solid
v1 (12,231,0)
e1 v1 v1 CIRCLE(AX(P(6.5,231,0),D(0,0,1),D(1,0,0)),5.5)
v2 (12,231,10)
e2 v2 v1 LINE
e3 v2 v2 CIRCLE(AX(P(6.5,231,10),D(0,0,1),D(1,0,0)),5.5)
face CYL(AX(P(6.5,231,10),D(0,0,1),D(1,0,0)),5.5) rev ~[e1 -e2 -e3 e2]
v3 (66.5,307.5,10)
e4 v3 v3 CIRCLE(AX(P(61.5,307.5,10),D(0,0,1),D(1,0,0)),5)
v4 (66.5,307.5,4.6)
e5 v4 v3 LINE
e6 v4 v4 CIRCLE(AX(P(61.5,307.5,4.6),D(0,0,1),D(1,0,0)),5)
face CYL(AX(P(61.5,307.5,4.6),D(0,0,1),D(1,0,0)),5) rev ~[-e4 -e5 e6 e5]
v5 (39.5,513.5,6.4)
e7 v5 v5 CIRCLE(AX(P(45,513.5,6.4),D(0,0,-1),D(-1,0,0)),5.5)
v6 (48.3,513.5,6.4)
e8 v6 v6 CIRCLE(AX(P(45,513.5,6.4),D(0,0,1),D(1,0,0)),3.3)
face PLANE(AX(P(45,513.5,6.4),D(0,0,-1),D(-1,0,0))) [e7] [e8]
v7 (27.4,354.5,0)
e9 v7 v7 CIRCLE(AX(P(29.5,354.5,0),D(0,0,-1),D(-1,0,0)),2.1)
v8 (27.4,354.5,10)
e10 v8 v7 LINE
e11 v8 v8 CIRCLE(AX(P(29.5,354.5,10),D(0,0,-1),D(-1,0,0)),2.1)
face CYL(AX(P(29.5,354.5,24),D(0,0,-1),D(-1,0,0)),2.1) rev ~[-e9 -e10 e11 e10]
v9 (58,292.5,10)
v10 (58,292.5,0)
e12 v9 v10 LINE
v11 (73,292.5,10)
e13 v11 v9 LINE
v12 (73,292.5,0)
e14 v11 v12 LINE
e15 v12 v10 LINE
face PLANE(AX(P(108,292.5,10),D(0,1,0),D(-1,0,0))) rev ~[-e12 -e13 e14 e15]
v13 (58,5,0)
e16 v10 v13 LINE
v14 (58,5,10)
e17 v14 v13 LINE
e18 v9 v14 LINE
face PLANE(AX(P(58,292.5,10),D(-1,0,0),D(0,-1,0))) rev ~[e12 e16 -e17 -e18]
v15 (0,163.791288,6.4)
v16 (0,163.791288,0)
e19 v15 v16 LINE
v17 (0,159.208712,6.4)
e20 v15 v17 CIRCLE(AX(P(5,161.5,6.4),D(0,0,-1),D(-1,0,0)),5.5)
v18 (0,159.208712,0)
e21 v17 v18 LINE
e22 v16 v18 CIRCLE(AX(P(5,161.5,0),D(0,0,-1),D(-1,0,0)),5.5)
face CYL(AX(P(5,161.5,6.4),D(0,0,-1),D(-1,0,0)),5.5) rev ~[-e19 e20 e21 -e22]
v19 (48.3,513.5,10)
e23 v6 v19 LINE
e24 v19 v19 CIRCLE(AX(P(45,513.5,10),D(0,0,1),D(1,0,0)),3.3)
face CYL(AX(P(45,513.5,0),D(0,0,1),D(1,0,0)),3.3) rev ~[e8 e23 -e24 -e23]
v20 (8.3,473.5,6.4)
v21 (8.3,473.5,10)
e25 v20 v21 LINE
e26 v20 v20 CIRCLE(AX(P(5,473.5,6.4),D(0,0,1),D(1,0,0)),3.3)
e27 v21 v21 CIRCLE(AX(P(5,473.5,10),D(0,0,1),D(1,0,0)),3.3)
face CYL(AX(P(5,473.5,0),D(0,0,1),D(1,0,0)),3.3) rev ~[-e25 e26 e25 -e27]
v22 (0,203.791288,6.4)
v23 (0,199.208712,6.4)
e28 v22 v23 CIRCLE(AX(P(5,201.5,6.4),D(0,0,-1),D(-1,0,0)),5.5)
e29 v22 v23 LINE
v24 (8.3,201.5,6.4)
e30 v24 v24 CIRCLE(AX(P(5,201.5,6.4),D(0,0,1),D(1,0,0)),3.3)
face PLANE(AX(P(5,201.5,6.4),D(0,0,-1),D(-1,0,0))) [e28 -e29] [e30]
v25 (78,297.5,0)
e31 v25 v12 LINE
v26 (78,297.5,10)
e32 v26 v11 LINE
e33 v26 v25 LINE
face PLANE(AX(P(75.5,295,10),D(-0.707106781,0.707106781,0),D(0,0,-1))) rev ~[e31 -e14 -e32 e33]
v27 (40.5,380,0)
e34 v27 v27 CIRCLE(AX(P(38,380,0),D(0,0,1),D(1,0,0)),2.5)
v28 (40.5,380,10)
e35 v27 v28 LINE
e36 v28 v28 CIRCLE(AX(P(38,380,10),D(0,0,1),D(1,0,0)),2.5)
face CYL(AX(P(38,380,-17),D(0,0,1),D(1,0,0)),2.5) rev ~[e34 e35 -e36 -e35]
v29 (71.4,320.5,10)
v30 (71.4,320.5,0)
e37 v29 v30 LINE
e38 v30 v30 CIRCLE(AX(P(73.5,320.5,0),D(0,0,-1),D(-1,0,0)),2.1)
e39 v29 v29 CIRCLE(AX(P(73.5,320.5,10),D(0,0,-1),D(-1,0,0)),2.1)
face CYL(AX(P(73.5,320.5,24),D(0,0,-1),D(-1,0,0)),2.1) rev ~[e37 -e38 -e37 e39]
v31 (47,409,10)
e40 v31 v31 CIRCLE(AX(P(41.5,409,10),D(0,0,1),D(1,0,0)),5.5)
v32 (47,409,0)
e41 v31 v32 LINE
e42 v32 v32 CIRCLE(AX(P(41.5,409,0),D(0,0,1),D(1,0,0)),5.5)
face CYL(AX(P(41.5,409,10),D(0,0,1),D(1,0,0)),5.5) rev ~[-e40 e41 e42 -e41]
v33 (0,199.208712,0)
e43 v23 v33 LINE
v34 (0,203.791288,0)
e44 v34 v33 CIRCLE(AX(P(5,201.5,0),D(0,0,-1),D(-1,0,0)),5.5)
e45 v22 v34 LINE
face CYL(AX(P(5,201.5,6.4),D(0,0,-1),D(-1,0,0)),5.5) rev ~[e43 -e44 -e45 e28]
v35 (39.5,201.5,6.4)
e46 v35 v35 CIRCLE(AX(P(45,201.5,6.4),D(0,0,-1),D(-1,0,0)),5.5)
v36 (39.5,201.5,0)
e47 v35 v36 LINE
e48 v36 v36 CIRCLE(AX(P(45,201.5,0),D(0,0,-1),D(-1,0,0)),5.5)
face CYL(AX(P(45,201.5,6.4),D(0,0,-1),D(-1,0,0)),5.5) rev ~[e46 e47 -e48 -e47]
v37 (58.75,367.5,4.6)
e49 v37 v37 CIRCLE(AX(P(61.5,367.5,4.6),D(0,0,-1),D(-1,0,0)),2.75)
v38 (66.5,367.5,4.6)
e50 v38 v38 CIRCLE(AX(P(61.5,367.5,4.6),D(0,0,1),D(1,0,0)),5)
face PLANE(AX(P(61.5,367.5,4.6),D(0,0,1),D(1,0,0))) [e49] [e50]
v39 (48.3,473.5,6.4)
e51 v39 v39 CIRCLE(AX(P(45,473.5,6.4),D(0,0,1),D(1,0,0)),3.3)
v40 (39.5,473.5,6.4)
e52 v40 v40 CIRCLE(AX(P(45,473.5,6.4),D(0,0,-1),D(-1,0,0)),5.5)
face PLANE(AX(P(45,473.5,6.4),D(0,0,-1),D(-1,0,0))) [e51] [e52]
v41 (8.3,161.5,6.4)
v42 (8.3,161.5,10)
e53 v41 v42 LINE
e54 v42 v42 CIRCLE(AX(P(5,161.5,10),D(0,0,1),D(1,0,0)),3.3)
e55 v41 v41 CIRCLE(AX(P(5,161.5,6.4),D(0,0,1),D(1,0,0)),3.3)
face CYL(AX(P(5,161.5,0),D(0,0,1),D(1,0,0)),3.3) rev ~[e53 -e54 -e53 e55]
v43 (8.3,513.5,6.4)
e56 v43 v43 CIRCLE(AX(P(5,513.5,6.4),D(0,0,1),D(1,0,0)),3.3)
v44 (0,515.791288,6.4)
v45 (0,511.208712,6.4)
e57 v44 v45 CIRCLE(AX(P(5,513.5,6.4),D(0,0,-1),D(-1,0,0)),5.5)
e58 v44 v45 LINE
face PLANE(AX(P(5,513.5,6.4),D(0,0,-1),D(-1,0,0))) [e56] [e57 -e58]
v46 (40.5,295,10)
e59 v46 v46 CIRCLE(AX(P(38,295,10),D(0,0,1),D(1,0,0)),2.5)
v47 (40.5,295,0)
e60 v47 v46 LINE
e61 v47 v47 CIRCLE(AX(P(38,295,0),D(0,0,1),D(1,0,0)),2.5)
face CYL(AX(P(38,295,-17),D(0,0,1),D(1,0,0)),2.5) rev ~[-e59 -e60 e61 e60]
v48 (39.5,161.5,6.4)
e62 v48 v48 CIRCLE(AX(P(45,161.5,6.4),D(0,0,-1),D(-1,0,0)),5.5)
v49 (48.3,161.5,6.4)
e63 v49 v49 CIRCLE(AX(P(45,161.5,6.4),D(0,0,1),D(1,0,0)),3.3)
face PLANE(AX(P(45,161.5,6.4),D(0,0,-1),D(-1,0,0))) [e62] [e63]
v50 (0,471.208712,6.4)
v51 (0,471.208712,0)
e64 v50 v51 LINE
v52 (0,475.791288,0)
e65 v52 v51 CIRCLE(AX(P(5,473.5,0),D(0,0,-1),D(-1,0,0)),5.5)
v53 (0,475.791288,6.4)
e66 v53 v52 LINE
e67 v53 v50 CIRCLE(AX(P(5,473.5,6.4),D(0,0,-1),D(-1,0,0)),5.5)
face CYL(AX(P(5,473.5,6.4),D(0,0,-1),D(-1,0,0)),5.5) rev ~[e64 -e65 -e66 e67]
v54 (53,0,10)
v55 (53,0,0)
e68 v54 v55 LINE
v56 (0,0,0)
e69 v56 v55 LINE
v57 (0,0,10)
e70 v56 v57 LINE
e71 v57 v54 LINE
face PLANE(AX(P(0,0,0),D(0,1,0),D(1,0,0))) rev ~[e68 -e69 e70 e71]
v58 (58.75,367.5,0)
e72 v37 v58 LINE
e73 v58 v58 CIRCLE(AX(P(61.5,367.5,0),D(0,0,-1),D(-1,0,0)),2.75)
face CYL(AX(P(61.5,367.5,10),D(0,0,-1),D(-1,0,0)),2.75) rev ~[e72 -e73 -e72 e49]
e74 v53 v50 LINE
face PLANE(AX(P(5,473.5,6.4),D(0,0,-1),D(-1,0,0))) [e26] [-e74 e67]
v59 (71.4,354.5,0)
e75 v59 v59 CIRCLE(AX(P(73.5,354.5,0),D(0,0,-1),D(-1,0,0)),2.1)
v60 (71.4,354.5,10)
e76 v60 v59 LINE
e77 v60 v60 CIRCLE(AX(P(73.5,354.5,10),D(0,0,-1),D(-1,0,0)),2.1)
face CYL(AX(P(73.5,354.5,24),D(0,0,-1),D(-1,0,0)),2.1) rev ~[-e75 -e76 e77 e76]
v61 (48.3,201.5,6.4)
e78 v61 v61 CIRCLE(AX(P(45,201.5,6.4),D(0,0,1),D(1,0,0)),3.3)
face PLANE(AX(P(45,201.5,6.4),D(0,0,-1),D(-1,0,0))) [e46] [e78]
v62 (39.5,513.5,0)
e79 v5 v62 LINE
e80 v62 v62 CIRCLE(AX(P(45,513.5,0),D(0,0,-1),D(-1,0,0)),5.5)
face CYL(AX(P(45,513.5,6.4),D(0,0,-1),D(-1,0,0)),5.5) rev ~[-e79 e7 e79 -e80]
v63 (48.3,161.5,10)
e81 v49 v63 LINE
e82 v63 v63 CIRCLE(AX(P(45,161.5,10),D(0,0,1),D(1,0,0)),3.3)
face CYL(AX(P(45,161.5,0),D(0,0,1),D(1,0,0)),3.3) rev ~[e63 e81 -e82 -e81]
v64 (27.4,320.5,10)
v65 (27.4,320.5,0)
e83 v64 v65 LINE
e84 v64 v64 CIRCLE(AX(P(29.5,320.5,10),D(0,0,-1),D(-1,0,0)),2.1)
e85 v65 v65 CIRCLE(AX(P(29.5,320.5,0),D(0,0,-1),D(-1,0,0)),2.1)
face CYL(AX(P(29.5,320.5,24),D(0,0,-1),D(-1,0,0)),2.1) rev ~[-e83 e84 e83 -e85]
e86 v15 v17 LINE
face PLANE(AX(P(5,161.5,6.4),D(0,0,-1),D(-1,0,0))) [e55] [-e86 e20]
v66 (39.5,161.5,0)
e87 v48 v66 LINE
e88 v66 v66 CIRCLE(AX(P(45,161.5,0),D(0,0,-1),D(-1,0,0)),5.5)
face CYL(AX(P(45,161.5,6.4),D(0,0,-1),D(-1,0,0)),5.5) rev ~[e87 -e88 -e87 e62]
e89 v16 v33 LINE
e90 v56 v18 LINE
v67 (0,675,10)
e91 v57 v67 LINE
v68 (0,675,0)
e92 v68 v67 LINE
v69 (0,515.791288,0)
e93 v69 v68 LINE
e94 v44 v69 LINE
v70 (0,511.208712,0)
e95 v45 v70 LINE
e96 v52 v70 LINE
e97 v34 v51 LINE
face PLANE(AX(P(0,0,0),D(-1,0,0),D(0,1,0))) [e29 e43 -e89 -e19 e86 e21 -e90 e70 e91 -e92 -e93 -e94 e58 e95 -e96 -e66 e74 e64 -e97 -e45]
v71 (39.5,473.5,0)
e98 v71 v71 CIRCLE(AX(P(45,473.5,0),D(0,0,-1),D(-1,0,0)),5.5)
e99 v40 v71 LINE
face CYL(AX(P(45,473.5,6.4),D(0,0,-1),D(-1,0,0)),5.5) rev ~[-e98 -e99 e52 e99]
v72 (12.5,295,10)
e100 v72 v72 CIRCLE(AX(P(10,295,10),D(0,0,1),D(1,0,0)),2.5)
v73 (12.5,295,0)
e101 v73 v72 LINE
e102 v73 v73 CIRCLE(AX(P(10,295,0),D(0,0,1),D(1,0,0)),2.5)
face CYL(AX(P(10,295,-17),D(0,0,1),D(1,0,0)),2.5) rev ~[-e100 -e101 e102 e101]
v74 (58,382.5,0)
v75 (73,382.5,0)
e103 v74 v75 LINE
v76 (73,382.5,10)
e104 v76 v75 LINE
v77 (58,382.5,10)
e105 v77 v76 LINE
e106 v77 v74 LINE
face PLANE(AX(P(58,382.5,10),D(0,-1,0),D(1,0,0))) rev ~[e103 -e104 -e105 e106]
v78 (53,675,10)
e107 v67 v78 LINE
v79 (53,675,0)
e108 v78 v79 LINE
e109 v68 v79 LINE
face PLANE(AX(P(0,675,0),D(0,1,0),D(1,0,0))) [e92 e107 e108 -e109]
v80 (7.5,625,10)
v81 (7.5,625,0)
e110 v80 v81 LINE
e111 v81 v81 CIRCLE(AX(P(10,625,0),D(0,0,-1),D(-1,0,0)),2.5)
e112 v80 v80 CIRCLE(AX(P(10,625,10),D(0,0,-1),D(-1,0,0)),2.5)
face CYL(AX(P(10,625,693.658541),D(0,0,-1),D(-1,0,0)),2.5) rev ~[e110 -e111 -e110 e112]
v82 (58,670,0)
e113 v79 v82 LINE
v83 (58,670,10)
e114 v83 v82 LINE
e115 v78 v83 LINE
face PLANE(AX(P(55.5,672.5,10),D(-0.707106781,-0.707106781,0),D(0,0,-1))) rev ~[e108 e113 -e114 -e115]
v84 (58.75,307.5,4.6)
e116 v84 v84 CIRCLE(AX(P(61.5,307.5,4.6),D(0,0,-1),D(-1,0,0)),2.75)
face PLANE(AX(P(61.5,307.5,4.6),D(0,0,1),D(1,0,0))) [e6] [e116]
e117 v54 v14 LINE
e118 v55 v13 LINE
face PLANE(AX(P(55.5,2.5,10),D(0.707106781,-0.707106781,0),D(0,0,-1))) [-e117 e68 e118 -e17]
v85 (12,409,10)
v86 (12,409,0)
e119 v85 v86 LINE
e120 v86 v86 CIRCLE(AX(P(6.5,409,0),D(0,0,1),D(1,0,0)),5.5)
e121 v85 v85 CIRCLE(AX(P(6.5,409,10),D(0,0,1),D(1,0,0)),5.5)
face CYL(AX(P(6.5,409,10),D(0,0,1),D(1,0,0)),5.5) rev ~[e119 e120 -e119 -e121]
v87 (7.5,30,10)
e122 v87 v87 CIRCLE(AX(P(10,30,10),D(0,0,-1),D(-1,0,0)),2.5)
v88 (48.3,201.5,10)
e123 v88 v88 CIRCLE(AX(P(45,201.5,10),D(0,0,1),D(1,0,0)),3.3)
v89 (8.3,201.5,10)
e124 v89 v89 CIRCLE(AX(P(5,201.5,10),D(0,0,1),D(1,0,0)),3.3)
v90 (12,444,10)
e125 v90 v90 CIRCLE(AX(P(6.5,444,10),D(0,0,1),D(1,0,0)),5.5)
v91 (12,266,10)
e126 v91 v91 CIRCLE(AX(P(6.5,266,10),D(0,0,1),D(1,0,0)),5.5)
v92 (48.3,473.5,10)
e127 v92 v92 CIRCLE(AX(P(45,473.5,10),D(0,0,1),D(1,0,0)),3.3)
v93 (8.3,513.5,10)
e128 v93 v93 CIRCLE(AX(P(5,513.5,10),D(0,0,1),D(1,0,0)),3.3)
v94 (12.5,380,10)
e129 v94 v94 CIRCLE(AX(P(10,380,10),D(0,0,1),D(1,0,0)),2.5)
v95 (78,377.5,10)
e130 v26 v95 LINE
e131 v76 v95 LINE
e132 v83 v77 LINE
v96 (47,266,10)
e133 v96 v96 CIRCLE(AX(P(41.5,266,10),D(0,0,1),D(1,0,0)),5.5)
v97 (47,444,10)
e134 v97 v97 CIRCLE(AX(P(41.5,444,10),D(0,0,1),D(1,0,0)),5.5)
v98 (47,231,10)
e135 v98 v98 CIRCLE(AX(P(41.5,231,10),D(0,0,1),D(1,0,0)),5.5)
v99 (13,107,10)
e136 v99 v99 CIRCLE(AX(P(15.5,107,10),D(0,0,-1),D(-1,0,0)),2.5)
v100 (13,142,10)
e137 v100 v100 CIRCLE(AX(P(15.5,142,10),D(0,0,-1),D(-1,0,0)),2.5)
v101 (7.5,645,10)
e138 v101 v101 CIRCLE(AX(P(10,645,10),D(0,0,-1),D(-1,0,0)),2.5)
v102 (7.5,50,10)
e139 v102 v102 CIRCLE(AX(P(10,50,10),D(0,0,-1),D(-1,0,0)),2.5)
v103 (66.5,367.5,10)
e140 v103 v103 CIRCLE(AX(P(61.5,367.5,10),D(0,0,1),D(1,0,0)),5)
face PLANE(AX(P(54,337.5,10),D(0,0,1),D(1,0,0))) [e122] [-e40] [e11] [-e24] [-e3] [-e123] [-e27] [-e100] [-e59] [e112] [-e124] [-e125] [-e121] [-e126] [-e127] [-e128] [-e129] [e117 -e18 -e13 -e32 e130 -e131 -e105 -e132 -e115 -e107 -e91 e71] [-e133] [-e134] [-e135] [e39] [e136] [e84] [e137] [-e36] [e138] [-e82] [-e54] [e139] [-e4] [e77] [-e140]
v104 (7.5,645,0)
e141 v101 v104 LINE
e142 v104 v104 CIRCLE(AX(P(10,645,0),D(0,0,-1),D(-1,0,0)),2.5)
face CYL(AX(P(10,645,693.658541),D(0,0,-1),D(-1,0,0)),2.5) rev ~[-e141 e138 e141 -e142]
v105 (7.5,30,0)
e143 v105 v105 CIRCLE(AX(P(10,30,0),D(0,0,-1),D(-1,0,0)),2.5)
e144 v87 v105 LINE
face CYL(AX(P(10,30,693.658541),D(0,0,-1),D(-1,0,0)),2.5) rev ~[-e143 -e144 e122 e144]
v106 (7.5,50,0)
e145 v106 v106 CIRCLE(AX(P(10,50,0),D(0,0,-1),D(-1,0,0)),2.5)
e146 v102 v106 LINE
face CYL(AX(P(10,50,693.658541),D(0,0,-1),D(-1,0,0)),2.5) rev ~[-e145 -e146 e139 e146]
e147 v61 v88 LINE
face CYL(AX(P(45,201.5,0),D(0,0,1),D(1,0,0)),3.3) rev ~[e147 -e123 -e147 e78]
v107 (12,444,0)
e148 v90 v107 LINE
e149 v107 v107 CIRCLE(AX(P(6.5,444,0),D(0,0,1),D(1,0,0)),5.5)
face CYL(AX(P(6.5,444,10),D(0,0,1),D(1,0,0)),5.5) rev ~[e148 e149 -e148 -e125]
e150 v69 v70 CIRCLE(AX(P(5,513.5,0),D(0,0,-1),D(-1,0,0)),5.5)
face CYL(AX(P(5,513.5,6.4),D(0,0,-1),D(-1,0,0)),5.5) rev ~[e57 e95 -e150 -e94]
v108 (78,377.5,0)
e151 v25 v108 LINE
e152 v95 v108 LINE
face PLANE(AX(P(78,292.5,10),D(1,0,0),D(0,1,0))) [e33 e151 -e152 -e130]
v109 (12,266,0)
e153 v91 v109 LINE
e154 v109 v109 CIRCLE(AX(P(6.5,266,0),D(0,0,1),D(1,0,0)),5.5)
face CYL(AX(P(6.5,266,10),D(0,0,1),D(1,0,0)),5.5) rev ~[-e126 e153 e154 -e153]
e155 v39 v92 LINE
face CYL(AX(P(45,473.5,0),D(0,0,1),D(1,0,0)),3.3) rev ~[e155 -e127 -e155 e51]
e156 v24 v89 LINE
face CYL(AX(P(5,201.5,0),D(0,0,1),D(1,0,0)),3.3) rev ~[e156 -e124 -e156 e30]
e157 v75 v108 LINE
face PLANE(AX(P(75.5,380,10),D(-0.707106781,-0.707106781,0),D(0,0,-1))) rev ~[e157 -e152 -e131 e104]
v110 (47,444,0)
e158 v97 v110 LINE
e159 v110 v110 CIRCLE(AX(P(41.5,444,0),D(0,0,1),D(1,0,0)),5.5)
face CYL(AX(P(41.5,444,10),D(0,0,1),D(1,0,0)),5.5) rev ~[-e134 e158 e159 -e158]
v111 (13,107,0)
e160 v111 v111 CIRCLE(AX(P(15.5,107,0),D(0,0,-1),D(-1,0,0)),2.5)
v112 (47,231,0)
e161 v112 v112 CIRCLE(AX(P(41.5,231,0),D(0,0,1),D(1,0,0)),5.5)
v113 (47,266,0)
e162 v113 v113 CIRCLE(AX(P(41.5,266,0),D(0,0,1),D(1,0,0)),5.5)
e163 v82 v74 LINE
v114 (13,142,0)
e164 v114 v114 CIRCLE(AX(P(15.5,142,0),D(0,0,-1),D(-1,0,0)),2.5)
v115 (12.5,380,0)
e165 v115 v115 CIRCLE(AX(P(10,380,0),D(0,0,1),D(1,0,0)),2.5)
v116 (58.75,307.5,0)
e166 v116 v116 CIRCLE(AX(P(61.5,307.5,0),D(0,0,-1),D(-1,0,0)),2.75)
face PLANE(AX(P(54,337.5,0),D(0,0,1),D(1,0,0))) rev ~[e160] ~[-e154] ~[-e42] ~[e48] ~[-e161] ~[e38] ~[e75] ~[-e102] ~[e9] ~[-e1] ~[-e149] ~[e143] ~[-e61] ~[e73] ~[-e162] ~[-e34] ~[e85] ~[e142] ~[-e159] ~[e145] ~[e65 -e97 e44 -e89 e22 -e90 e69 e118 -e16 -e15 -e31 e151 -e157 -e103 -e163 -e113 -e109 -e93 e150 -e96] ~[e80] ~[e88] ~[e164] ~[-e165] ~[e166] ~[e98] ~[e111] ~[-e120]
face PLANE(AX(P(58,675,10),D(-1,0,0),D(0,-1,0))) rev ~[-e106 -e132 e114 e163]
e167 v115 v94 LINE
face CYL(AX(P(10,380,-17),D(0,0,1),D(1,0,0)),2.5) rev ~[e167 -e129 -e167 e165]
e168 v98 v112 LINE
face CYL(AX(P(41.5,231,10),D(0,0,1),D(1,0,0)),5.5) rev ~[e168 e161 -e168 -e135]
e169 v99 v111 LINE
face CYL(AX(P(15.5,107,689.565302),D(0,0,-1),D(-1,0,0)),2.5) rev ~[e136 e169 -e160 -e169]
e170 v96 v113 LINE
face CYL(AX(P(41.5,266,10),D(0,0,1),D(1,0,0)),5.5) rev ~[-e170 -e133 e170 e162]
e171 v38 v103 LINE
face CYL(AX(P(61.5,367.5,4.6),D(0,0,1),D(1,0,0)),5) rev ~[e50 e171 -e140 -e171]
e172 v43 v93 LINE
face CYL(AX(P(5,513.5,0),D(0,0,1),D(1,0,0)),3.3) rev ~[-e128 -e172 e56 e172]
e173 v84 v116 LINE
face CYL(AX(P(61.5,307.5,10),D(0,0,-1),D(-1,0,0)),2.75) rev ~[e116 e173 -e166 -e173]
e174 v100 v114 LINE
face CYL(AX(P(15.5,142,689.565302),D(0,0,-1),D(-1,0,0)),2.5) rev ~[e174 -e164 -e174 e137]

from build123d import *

# Parameters (mm, degrees)
SKETCH_1_W                     = 108
SKETCH_1_H                     = 675
EXTRUDE_1_DEPTH                = 10
HOLE_WIZARD_M6_1_D             = 5
HOLE_WIZARD_M6_1_2_D           = 6.6
HOLE_WIZARD_M6_1_2_CBORE_D     = 11
HOLE_WIZARD_M6_1_2_CBORE_DEPTH = 6.4
HOLE_WIZARD_M5_1_D             = 4.2
HOLE_WIZARD_M5_1_DEPTH         = 14
HOLE_WIZARD_M5_1_TIP           = 1.2618073
HOLE_WIZARD_M6_2_D             = 5
HOLE_WIZARD_M6_2_DEPTH         = 17
HOLE_WIZARD_M6_2_TIP           = 1.502151548
HOLE_WIZARD_M5_1_2_D           = 5.5
HOLE_WIZARD_M5_1_2_DEPTH       = 14
HOLE_WIZARD_M5_1_2_CBORE_D     = 10
HOLE_WIZARD_M5_1_2_CBORE_DEPTH = 5.4
HOLE_WIZARD_M5_1_2_TIP         = 1.652366702
HOLE_WIZARD_M6_3_D             = 5
HOLE_WIZARD_M6_3_DEPTH         = 17
HOLE_WIZARD_M6_3_TIP           = 1.502151548
SKETCH_14_R                    = 5.5
CUT_EXTRUDE_1_DEPTH            = 60
SKETCH_15_R                    = 2.5
SKETCH_15_W                    = 30
SKETCH_15_H                    = 90
SKETCH_15_R_2                  = 5
CUT_EXTRUDE_2_DEPTH            = 684.658540501
CHAMFER_1_SIZE                 = 5
HOLE_WIZARD_M6_4_D             = 5


with BuildPart() as part:
    # 草图1 → 凸台-拉伸1 (new body)
    with BuildSketch(Plane.XY):
        with Locations((54, 337.5)):
            Rectangle(SKETCH_1_W, SKETCH_1_H)
    extrude(amount=EXTRUDE_1_DEPTH)

    # Hole Wizard M6 _1 (through all)
    with Locations(Plane.XY.offset(10)):
        with Locations((10, 645), (10, 625), (10, 50), (10, 30)):
            Hole(HOLE_WIZARD_M6_1_D / 2)

    # Hole Wizard M6 _1 2 (through all)
    with Locations(Plane(origin=(0, 0, 0), x_dir=(-1, 0, 0), z_dir=(0, 0, -1))):
        with Locations((-45, 513.5), (-5, 513.5), (-45, 473.5), (-5, 473.5), (-5, 201.5), (-45, 201.5), (-5, 161.5), (-45, 161.5)):
            CounterBoreHole(HOLE_WIZARD_M6_1_2_D / 2, HOLE_WIZARD_M6_1_2_CBORE_D / 2, HOLE_WIZARD_M6_1_2_CBORE_DEPTH)

    # Hole Wizard M5 _1
    with Locations(Plane.XY.offset(10)):
        with Locations((29.5, 354.5), (73.5, 354.5), (29.5, 320.5), (73.5, 320.5)):
            Hole(HOLE_WIZARD_M5_1_D / 2, depth=HOLE_WIZARD_M5_1_DEPTH)
            with Locations((0, 0, -(HOLE_WIZARD_M5_1_DEPTH + HOLE_WIZARD_M5_1_TIP / 2))):  # 118° drill point
                Cone(0, HOLE_WIZARD_M5_1_D / 2, HOLE_WIZARD_M5_1_TIP, mode=Mode.SUBTRACT)

    # M6 螺纹孔2
    with Locations(Plane.XY.offset(10)):
        with Locations((97.5, 431.5), (97.5, 396.5)):
            Hole(HOLE_WIZARD_M6_2_D / 2, depth=HOLE_WIZARD_M6_2_DEPTH)
            with Locations((0, 0, -(HOLE_WIZARD_M6_2_DEPTH + HOLE_WIZARD_M6_2_TIP / 2))):  # 118° drill point
                Cone(0, HOLE_WIZARD_M6_2_D / 2, HOLE_WIZARD_M6_2_TIP, mode=Mode.SUBTRACT)

    # Hole Wizard M5 _1 2
    with Locations(Plane.XY.offset(10)):
        with Locations((61.5, 367.5), (91.5, 367.5), (61.5, 307.5), (91.5, 307.5)):
            CounterBoreHole(HOLE_WIZARD_M5_1_2_D / 2, HOLE_WIZARD_M5_1_2_CBORE_D / 2, HOLE_WIZARD_M5_1_2_CBORE_DEPTH, depth=HOLE_WIZARD_M5_1_2_DEPTH)
            with Locations((0, 0, -(HOLE_WIZARD_M5_1_2_DEPTH + HOLE_WIZARD_M5_1_2_TIP / 2))):  # 118° drill point
                Cone(0, HOLE_WIZARD_M5_1_2_D / 2, HOLE_WIZARD_M5_1_2_TIP, mode=Mode.SUBTRACT)

    # M6 螺纹孔3
    with Locations(Plane(origin=(0, 0, 0), x_dir=(-1, 0, 0), z_dir=(0, 0, -1))):
        with Locations((-38, 380), (-10, 380), (-38, 295), (-10, 295)):
            Hole(HOLE_WIZARD_M6_3_D / 2, depth=HOLE_WIZARD_M6_3_DEPTH)
            with Locations((0, 0, -(HOLE_WIZARD_M6_3_DEPTH + HOLE_WIZARD_M6_3_TIP / 2))):  # 118° drill point
                Cone(0, HOLE_WIZARD_M6_3_D / 2, HOLE_WIZARD_M6_3_TIP, mode=Mode.SUBTRACT)

    # 草图14 → 切除-拉伸1 (cut)
    with BuildSketch(Plane.XY.offset(10)):
        with Locations((41.5, 444)):
            Circle(SKETCH_14_R)
        with Locations((6.5, 444)):
            Circle(SKETCH_14_R)
        with Locations((41.5, 409)):
            Circle(SKETCH_14_R)
        with Locations((6.5, 409)):
            Circle(SKETCH_14_R)
        with Locations((41.5, 266)):
            Circle(SKETCH_14_R)
        with Locations((41.5, 231)):
            Circle(SKETCH_14_R)
        with Locations((6.5, 231)):
            Circle(SKETCH_14_R)
        with Locations((6.5, 266)):
            Circle(SKETCH_14_R)
    extrude(amount=-CUT_EXTRUDE_1_DEPTH, mode=Mode.SUBTRACT)

    # 草图15 → 切除-拉伸2 (cut, through all)
    # profile 1 of 5: a face of its own
    with BuildSketch(Plane.XY.offset(10)):
        Polygon((108, 382.5), (108, 675), (58, 675), (58, 382.5), (78, 382.5), align=None)
        with Locations((97.5, 396.5)):
            Circle(SKETCH_15_R, mode=Mode.SUBTRACT)
        with Locations((97.5, 431.5)):
            Circle(SKETCH_15_R, mode=Mode.SUBTRACT)
    # profile 2 of 5: a face of its own
    with BuildSketch(Plane.XY.offset(10)):
        with Locations((93, 337.5)):
            Rectangle(SKETCH_15_W, SKETCH_15_H)
        with Locations((91.5, 307.5)):
            Circle(SKETCH_15_R_2, mode=Mode.SUBTRACT)
        with Locations((91.5, 367.5)):
            Circle(SKETCH_15_R_2, mode=Mode.SUBTRACT)
    # profile 3 of 5: a face of its own
    with BuildSketch(Plane.XY.offset(10)):
        Polygon((108, 0), (108, 292.5), (78, 292.5), (58, 292.5), (58, 0), align=None)
    # profile 4 of 5: a face of its own
    with BuildSketch(Plane.XY.offset(10)):
        with Locations((91.5, 367.5)):
            Circle(SKETCH_15_R_2)
    # profile 5 of 5: a face of its own
    with BuildSketch(Plane.XY.offset(10)):
        with Locations((91.5, 307.5)):
            Circle(SKETCH_15_R_2)
    extrude(amount=-CUT_EXTRUDE_2_DEPTH, mode=Mode.SUBTRACT)

    # 倒角1
    chamfer_1_edges = [part.edges().sort_by_distance(p)[0] for p in [
        (58, 675, 5),
        (58, 0, 5),
        (78, 292.5, 5),
        (78, 382.5, 5),
    ]]
    chamfer(chamfer_1_edges, length=CHAMFER_1_SIZE)

    # M6 螺纹孔4 (through all)
    with Locations(Plane.XY.offset(10)):
        with Locations((15.5, 142), (15.5, 107)):
            Hole(HOLE_WIZARD_M6_4_D / 2)


solid = part.part
